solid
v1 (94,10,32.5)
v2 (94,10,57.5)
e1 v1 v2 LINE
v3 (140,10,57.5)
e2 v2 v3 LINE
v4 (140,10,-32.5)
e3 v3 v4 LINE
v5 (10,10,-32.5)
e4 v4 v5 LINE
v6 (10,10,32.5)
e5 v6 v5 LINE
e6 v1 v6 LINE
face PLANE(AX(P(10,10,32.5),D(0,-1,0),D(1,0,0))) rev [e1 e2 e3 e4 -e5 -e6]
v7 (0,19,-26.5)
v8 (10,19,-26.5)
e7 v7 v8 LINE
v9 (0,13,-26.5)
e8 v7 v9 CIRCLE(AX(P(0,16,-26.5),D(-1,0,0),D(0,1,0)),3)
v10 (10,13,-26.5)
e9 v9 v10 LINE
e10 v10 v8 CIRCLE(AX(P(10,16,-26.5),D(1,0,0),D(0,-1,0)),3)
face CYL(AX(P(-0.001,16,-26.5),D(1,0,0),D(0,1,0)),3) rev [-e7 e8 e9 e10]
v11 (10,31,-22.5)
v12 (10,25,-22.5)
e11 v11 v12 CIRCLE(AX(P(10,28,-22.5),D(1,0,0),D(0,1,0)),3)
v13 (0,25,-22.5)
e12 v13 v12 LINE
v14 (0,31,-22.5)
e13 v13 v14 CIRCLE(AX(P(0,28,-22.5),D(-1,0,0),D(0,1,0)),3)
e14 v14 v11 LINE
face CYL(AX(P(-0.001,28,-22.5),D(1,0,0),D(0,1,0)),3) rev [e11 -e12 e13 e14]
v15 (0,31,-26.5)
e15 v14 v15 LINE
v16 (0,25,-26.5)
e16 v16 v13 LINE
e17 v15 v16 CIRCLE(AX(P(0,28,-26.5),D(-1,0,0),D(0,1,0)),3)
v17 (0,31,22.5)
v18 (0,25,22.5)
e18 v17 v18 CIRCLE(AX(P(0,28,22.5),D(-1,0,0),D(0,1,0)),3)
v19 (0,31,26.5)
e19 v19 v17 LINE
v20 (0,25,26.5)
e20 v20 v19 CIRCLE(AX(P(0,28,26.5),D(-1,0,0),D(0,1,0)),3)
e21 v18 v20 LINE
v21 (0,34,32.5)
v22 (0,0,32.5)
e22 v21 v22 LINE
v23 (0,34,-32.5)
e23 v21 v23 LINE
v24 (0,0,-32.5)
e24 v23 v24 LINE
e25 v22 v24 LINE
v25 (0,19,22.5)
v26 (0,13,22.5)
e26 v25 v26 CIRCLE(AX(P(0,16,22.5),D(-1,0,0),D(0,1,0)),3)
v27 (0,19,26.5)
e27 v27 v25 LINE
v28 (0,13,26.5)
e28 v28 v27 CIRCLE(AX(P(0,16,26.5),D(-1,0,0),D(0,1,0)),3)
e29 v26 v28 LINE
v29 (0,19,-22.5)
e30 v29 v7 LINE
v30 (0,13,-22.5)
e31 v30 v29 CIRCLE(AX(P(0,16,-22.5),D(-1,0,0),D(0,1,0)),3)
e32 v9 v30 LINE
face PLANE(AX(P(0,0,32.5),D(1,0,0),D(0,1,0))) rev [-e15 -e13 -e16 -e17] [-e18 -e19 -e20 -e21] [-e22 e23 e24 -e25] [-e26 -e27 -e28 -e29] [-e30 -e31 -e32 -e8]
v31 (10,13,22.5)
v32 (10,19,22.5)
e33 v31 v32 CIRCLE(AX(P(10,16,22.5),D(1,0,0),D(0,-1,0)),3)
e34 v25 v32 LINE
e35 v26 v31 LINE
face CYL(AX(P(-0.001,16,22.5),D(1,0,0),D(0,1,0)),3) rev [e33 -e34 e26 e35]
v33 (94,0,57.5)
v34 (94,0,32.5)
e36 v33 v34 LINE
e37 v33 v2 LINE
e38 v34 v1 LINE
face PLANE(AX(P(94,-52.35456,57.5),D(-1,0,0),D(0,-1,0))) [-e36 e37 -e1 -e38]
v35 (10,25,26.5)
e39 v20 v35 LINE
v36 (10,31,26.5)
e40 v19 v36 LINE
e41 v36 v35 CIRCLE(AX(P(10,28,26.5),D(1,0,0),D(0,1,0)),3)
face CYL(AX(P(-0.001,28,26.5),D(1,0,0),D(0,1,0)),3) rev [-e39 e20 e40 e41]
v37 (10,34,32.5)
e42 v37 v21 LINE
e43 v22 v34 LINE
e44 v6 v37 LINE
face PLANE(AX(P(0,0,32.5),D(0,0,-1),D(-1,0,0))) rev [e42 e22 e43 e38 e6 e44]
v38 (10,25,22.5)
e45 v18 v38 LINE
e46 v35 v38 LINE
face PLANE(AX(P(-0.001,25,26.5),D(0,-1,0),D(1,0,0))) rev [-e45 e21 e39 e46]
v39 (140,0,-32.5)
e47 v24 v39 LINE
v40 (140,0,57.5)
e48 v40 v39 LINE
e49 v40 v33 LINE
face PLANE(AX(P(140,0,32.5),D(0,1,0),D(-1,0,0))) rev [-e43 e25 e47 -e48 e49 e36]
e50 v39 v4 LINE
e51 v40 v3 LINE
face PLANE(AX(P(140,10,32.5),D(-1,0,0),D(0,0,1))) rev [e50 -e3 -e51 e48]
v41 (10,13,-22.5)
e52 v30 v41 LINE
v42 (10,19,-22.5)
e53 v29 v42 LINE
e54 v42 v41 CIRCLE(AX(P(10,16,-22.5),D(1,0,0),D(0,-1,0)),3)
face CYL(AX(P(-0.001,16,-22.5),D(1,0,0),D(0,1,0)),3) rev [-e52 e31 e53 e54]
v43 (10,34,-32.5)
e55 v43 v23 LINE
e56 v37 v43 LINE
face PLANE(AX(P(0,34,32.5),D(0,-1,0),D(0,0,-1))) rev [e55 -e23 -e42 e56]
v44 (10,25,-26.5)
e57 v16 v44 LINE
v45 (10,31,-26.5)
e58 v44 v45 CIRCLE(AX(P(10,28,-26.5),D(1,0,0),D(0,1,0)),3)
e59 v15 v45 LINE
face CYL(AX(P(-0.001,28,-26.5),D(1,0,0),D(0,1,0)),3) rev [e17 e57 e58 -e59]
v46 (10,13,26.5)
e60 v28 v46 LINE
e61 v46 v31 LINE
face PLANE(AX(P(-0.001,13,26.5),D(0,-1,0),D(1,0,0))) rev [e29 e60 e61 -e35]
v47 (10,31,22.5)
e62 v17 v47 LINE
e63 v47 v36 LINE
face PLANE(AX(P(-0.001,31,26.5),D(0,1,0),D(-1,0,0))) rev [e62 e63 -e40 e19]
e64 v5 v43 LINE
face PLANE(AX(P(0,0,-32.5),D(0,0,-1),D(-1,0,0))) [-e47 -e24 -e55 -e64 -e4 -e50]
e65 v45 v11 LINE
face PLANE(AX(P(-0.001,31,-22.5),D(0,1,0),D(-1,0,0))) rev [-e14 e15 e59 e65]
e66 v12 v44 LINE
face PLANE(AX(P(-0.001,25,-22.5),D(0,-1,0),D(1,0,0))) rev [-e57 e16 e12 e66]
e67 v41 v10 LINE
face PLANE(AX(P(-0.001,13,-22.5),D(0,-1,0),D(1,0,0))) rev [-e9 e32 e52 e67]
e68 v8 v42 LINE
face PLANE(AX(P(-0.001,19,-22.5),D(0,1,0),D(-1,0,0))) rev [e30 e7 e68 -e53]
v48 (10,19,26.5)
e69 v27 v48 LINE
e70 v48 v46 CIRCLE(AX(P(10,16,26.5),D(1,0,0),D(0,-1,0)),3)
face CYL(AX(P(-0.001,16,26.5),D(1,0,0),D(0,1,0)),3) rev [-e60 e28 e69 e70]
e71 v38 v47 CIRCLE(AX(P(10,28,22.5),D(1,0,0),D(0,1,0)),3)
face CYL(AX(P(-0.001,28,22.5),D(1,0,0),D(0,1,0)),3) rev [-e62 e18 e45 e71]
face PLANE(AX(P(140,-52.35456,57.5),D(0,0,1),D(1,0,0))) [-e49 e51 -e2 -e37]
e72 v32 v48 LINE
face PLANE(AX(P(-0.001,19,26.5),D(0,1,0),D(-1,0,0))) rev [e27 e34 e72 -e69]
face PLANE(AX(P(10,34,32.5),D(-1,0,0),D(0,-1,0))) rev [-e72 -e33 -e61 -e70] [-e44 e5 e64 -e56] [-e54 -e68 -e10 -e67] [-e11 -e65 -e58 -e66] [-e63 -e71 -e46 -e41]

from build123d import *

# Parameters (mm, degrees)
EXTRUDE_1_DEPTH     = 32.5
CUT_EXTRUDE_1_REACH = 140.247
SKETCH_3_W          = 46
SKETCH_3_H          = 25
EXTRUDE_2_DEPTH     = 10


with BuildPart() as part:
    # 草图1 → 凸台-拉伸1 (new, symmetric)
    with BuildSketch(Plane.XY):
        Polygon((0, 0), (0, 34), (10, 34), (10, 10), (140, 10), (140, 0), align=None)
    extrude(amount=EXTRUDE_1_DEPTH, both=True)

    # 草图2 → 切除-拉伸1 (cut, up to next)
    with BuildSketch(Plane(origin=(10, 0, 0), x_dir=(0, 0, -1), z_dir=(1, 0, 0)), mode=Mode.PRIVATE) as cut_extrude_1_sk1:
        with BuildLine():
            Line((-26.5, 31), (-22.5, 31))
            ThreePointArc((-22.5, 31), (-19.5, 28), (-22.5, 25))
            Line((-22.5, 25), (-26.5, 25))
            ThreePointArc((-26.5, 25), (-29.5, 28), (-26.5, 31))
        make_face()
    cut_extrude_1_tool1 = extrude(cut_extrude_1_sk1.sketch, amount=-CUT_EXTRUDE_1_REACH, mode=Mode.PRIVATE) & part.part
    # 草图2 → 切除-拉伸1 (cut, up to next)
    with BuildSketch(Plane(origin=(10, 0, 0), x_dir=(0, 0, -1), z_dir=(1, 0, 0)), mode=Mode.PRIVATE) as cut_extrude_1_sk2:
        with BuildLine():
            Line((22.5, 31), (26.5, 31))
            ThreePointArc((26.5, 31), (29.5, 28), (26.5, 25))
            Line((26.5, 25), (22.5, 25))
            ThreePointArc((22.5, 25), (19.5, 28), (22.5, 31))
        make_face()
    cut_extrude_1_tool2 = extrude(cut_extrude_1_sk2.sketch, amount=-CUT_EXTRUDE_1_REACH, mode=Mode.PRIVATE) & part.part
    # 草图2 → 切除-拉伸1 (cut, up to next)
    with BuildSketch(Plane(origin=(10, 0, 0), x_dir=(0, 0, -1), z_dir=(1, 0, 0)), mode=Mode.PRIVATE) as cut_extrude_1_sk3:
        with BuildLine():
            Line((-26.5, 13), (-22.5, 13))
            ThreePointArc((-22.5, 13), (-19.5, 16), (-22.5, 19))
            Line((-22.5, 19), (-26.5, 19))
            ThreePointArc((-26.5, 19), (-29.5, 16), (-26.5, 13))
        make_face()
    cut_extrude_1_tool3 = extrude(cut_extrude_1_sk3.sketch, amount=-CUT_EXTRUDE_1_REACH, mode=Mode.PRIVATE) & part.part
    # 草图2 → 切除-拉伸1 (cut, up to next)
    with BuildSketch(Plane(origin=(10, 0, 0), x_dir=(0, 0, -1), z_dir=(1, 0, 0)), mode=Mode.PRIVATE) as cut_extrude_1_sk4:
        with BuildLine():
            Line((22.5, 13), (26.5, 13))
            ThreePointArc((26.5, 13), (29.5, 16), (26.5, 19))
            Line((26.5, 19), (22.5, 19))
            ThreePointArc((22.5, 19), (19.5, 16), (22.5, 13))
        make_face()
    cut_extrude_1_tool4 = extrude(cut_extrude_1_sk4.sketch, amount=-CUT_EXTRUDE_1_REACH, mode=Mode.PRIVATE) & part.part
    add(cut_extrude_1_tool1.solids().sort_by_distance((10, 28, 24.5))[0], mode=Mode.SUBTRACT)
    add(cut_extrude_1_tool2.solids().sort_by_distance((10, 28, -24.5))[0], mode=Mode.SUBTRACT)
    add(cut_extrude_1_tool3.solids().sort_by_distance((10, 16, 24.5))[0], mode=Mode.SUBTRACT)
    add(cut_extrude_1_tool4.solids().sort_by_distance((10, 16, -24.5))[0], mode=Mode.SUBTRACT)

    # 草图3 → 凸台-拉伸2 (add)
    with BuildSketch(Plane(origin=(0, 10, 0), x_dir=(1, 0, 0), z_dir=(0, 1, 0))):
        with Locations((117, -45)):
            Rectangle(SKETCH_3_W, SKETCH_3_H)
    extrude(amount=-EXTRUDE_2_DEPTH)


solid = part.part
